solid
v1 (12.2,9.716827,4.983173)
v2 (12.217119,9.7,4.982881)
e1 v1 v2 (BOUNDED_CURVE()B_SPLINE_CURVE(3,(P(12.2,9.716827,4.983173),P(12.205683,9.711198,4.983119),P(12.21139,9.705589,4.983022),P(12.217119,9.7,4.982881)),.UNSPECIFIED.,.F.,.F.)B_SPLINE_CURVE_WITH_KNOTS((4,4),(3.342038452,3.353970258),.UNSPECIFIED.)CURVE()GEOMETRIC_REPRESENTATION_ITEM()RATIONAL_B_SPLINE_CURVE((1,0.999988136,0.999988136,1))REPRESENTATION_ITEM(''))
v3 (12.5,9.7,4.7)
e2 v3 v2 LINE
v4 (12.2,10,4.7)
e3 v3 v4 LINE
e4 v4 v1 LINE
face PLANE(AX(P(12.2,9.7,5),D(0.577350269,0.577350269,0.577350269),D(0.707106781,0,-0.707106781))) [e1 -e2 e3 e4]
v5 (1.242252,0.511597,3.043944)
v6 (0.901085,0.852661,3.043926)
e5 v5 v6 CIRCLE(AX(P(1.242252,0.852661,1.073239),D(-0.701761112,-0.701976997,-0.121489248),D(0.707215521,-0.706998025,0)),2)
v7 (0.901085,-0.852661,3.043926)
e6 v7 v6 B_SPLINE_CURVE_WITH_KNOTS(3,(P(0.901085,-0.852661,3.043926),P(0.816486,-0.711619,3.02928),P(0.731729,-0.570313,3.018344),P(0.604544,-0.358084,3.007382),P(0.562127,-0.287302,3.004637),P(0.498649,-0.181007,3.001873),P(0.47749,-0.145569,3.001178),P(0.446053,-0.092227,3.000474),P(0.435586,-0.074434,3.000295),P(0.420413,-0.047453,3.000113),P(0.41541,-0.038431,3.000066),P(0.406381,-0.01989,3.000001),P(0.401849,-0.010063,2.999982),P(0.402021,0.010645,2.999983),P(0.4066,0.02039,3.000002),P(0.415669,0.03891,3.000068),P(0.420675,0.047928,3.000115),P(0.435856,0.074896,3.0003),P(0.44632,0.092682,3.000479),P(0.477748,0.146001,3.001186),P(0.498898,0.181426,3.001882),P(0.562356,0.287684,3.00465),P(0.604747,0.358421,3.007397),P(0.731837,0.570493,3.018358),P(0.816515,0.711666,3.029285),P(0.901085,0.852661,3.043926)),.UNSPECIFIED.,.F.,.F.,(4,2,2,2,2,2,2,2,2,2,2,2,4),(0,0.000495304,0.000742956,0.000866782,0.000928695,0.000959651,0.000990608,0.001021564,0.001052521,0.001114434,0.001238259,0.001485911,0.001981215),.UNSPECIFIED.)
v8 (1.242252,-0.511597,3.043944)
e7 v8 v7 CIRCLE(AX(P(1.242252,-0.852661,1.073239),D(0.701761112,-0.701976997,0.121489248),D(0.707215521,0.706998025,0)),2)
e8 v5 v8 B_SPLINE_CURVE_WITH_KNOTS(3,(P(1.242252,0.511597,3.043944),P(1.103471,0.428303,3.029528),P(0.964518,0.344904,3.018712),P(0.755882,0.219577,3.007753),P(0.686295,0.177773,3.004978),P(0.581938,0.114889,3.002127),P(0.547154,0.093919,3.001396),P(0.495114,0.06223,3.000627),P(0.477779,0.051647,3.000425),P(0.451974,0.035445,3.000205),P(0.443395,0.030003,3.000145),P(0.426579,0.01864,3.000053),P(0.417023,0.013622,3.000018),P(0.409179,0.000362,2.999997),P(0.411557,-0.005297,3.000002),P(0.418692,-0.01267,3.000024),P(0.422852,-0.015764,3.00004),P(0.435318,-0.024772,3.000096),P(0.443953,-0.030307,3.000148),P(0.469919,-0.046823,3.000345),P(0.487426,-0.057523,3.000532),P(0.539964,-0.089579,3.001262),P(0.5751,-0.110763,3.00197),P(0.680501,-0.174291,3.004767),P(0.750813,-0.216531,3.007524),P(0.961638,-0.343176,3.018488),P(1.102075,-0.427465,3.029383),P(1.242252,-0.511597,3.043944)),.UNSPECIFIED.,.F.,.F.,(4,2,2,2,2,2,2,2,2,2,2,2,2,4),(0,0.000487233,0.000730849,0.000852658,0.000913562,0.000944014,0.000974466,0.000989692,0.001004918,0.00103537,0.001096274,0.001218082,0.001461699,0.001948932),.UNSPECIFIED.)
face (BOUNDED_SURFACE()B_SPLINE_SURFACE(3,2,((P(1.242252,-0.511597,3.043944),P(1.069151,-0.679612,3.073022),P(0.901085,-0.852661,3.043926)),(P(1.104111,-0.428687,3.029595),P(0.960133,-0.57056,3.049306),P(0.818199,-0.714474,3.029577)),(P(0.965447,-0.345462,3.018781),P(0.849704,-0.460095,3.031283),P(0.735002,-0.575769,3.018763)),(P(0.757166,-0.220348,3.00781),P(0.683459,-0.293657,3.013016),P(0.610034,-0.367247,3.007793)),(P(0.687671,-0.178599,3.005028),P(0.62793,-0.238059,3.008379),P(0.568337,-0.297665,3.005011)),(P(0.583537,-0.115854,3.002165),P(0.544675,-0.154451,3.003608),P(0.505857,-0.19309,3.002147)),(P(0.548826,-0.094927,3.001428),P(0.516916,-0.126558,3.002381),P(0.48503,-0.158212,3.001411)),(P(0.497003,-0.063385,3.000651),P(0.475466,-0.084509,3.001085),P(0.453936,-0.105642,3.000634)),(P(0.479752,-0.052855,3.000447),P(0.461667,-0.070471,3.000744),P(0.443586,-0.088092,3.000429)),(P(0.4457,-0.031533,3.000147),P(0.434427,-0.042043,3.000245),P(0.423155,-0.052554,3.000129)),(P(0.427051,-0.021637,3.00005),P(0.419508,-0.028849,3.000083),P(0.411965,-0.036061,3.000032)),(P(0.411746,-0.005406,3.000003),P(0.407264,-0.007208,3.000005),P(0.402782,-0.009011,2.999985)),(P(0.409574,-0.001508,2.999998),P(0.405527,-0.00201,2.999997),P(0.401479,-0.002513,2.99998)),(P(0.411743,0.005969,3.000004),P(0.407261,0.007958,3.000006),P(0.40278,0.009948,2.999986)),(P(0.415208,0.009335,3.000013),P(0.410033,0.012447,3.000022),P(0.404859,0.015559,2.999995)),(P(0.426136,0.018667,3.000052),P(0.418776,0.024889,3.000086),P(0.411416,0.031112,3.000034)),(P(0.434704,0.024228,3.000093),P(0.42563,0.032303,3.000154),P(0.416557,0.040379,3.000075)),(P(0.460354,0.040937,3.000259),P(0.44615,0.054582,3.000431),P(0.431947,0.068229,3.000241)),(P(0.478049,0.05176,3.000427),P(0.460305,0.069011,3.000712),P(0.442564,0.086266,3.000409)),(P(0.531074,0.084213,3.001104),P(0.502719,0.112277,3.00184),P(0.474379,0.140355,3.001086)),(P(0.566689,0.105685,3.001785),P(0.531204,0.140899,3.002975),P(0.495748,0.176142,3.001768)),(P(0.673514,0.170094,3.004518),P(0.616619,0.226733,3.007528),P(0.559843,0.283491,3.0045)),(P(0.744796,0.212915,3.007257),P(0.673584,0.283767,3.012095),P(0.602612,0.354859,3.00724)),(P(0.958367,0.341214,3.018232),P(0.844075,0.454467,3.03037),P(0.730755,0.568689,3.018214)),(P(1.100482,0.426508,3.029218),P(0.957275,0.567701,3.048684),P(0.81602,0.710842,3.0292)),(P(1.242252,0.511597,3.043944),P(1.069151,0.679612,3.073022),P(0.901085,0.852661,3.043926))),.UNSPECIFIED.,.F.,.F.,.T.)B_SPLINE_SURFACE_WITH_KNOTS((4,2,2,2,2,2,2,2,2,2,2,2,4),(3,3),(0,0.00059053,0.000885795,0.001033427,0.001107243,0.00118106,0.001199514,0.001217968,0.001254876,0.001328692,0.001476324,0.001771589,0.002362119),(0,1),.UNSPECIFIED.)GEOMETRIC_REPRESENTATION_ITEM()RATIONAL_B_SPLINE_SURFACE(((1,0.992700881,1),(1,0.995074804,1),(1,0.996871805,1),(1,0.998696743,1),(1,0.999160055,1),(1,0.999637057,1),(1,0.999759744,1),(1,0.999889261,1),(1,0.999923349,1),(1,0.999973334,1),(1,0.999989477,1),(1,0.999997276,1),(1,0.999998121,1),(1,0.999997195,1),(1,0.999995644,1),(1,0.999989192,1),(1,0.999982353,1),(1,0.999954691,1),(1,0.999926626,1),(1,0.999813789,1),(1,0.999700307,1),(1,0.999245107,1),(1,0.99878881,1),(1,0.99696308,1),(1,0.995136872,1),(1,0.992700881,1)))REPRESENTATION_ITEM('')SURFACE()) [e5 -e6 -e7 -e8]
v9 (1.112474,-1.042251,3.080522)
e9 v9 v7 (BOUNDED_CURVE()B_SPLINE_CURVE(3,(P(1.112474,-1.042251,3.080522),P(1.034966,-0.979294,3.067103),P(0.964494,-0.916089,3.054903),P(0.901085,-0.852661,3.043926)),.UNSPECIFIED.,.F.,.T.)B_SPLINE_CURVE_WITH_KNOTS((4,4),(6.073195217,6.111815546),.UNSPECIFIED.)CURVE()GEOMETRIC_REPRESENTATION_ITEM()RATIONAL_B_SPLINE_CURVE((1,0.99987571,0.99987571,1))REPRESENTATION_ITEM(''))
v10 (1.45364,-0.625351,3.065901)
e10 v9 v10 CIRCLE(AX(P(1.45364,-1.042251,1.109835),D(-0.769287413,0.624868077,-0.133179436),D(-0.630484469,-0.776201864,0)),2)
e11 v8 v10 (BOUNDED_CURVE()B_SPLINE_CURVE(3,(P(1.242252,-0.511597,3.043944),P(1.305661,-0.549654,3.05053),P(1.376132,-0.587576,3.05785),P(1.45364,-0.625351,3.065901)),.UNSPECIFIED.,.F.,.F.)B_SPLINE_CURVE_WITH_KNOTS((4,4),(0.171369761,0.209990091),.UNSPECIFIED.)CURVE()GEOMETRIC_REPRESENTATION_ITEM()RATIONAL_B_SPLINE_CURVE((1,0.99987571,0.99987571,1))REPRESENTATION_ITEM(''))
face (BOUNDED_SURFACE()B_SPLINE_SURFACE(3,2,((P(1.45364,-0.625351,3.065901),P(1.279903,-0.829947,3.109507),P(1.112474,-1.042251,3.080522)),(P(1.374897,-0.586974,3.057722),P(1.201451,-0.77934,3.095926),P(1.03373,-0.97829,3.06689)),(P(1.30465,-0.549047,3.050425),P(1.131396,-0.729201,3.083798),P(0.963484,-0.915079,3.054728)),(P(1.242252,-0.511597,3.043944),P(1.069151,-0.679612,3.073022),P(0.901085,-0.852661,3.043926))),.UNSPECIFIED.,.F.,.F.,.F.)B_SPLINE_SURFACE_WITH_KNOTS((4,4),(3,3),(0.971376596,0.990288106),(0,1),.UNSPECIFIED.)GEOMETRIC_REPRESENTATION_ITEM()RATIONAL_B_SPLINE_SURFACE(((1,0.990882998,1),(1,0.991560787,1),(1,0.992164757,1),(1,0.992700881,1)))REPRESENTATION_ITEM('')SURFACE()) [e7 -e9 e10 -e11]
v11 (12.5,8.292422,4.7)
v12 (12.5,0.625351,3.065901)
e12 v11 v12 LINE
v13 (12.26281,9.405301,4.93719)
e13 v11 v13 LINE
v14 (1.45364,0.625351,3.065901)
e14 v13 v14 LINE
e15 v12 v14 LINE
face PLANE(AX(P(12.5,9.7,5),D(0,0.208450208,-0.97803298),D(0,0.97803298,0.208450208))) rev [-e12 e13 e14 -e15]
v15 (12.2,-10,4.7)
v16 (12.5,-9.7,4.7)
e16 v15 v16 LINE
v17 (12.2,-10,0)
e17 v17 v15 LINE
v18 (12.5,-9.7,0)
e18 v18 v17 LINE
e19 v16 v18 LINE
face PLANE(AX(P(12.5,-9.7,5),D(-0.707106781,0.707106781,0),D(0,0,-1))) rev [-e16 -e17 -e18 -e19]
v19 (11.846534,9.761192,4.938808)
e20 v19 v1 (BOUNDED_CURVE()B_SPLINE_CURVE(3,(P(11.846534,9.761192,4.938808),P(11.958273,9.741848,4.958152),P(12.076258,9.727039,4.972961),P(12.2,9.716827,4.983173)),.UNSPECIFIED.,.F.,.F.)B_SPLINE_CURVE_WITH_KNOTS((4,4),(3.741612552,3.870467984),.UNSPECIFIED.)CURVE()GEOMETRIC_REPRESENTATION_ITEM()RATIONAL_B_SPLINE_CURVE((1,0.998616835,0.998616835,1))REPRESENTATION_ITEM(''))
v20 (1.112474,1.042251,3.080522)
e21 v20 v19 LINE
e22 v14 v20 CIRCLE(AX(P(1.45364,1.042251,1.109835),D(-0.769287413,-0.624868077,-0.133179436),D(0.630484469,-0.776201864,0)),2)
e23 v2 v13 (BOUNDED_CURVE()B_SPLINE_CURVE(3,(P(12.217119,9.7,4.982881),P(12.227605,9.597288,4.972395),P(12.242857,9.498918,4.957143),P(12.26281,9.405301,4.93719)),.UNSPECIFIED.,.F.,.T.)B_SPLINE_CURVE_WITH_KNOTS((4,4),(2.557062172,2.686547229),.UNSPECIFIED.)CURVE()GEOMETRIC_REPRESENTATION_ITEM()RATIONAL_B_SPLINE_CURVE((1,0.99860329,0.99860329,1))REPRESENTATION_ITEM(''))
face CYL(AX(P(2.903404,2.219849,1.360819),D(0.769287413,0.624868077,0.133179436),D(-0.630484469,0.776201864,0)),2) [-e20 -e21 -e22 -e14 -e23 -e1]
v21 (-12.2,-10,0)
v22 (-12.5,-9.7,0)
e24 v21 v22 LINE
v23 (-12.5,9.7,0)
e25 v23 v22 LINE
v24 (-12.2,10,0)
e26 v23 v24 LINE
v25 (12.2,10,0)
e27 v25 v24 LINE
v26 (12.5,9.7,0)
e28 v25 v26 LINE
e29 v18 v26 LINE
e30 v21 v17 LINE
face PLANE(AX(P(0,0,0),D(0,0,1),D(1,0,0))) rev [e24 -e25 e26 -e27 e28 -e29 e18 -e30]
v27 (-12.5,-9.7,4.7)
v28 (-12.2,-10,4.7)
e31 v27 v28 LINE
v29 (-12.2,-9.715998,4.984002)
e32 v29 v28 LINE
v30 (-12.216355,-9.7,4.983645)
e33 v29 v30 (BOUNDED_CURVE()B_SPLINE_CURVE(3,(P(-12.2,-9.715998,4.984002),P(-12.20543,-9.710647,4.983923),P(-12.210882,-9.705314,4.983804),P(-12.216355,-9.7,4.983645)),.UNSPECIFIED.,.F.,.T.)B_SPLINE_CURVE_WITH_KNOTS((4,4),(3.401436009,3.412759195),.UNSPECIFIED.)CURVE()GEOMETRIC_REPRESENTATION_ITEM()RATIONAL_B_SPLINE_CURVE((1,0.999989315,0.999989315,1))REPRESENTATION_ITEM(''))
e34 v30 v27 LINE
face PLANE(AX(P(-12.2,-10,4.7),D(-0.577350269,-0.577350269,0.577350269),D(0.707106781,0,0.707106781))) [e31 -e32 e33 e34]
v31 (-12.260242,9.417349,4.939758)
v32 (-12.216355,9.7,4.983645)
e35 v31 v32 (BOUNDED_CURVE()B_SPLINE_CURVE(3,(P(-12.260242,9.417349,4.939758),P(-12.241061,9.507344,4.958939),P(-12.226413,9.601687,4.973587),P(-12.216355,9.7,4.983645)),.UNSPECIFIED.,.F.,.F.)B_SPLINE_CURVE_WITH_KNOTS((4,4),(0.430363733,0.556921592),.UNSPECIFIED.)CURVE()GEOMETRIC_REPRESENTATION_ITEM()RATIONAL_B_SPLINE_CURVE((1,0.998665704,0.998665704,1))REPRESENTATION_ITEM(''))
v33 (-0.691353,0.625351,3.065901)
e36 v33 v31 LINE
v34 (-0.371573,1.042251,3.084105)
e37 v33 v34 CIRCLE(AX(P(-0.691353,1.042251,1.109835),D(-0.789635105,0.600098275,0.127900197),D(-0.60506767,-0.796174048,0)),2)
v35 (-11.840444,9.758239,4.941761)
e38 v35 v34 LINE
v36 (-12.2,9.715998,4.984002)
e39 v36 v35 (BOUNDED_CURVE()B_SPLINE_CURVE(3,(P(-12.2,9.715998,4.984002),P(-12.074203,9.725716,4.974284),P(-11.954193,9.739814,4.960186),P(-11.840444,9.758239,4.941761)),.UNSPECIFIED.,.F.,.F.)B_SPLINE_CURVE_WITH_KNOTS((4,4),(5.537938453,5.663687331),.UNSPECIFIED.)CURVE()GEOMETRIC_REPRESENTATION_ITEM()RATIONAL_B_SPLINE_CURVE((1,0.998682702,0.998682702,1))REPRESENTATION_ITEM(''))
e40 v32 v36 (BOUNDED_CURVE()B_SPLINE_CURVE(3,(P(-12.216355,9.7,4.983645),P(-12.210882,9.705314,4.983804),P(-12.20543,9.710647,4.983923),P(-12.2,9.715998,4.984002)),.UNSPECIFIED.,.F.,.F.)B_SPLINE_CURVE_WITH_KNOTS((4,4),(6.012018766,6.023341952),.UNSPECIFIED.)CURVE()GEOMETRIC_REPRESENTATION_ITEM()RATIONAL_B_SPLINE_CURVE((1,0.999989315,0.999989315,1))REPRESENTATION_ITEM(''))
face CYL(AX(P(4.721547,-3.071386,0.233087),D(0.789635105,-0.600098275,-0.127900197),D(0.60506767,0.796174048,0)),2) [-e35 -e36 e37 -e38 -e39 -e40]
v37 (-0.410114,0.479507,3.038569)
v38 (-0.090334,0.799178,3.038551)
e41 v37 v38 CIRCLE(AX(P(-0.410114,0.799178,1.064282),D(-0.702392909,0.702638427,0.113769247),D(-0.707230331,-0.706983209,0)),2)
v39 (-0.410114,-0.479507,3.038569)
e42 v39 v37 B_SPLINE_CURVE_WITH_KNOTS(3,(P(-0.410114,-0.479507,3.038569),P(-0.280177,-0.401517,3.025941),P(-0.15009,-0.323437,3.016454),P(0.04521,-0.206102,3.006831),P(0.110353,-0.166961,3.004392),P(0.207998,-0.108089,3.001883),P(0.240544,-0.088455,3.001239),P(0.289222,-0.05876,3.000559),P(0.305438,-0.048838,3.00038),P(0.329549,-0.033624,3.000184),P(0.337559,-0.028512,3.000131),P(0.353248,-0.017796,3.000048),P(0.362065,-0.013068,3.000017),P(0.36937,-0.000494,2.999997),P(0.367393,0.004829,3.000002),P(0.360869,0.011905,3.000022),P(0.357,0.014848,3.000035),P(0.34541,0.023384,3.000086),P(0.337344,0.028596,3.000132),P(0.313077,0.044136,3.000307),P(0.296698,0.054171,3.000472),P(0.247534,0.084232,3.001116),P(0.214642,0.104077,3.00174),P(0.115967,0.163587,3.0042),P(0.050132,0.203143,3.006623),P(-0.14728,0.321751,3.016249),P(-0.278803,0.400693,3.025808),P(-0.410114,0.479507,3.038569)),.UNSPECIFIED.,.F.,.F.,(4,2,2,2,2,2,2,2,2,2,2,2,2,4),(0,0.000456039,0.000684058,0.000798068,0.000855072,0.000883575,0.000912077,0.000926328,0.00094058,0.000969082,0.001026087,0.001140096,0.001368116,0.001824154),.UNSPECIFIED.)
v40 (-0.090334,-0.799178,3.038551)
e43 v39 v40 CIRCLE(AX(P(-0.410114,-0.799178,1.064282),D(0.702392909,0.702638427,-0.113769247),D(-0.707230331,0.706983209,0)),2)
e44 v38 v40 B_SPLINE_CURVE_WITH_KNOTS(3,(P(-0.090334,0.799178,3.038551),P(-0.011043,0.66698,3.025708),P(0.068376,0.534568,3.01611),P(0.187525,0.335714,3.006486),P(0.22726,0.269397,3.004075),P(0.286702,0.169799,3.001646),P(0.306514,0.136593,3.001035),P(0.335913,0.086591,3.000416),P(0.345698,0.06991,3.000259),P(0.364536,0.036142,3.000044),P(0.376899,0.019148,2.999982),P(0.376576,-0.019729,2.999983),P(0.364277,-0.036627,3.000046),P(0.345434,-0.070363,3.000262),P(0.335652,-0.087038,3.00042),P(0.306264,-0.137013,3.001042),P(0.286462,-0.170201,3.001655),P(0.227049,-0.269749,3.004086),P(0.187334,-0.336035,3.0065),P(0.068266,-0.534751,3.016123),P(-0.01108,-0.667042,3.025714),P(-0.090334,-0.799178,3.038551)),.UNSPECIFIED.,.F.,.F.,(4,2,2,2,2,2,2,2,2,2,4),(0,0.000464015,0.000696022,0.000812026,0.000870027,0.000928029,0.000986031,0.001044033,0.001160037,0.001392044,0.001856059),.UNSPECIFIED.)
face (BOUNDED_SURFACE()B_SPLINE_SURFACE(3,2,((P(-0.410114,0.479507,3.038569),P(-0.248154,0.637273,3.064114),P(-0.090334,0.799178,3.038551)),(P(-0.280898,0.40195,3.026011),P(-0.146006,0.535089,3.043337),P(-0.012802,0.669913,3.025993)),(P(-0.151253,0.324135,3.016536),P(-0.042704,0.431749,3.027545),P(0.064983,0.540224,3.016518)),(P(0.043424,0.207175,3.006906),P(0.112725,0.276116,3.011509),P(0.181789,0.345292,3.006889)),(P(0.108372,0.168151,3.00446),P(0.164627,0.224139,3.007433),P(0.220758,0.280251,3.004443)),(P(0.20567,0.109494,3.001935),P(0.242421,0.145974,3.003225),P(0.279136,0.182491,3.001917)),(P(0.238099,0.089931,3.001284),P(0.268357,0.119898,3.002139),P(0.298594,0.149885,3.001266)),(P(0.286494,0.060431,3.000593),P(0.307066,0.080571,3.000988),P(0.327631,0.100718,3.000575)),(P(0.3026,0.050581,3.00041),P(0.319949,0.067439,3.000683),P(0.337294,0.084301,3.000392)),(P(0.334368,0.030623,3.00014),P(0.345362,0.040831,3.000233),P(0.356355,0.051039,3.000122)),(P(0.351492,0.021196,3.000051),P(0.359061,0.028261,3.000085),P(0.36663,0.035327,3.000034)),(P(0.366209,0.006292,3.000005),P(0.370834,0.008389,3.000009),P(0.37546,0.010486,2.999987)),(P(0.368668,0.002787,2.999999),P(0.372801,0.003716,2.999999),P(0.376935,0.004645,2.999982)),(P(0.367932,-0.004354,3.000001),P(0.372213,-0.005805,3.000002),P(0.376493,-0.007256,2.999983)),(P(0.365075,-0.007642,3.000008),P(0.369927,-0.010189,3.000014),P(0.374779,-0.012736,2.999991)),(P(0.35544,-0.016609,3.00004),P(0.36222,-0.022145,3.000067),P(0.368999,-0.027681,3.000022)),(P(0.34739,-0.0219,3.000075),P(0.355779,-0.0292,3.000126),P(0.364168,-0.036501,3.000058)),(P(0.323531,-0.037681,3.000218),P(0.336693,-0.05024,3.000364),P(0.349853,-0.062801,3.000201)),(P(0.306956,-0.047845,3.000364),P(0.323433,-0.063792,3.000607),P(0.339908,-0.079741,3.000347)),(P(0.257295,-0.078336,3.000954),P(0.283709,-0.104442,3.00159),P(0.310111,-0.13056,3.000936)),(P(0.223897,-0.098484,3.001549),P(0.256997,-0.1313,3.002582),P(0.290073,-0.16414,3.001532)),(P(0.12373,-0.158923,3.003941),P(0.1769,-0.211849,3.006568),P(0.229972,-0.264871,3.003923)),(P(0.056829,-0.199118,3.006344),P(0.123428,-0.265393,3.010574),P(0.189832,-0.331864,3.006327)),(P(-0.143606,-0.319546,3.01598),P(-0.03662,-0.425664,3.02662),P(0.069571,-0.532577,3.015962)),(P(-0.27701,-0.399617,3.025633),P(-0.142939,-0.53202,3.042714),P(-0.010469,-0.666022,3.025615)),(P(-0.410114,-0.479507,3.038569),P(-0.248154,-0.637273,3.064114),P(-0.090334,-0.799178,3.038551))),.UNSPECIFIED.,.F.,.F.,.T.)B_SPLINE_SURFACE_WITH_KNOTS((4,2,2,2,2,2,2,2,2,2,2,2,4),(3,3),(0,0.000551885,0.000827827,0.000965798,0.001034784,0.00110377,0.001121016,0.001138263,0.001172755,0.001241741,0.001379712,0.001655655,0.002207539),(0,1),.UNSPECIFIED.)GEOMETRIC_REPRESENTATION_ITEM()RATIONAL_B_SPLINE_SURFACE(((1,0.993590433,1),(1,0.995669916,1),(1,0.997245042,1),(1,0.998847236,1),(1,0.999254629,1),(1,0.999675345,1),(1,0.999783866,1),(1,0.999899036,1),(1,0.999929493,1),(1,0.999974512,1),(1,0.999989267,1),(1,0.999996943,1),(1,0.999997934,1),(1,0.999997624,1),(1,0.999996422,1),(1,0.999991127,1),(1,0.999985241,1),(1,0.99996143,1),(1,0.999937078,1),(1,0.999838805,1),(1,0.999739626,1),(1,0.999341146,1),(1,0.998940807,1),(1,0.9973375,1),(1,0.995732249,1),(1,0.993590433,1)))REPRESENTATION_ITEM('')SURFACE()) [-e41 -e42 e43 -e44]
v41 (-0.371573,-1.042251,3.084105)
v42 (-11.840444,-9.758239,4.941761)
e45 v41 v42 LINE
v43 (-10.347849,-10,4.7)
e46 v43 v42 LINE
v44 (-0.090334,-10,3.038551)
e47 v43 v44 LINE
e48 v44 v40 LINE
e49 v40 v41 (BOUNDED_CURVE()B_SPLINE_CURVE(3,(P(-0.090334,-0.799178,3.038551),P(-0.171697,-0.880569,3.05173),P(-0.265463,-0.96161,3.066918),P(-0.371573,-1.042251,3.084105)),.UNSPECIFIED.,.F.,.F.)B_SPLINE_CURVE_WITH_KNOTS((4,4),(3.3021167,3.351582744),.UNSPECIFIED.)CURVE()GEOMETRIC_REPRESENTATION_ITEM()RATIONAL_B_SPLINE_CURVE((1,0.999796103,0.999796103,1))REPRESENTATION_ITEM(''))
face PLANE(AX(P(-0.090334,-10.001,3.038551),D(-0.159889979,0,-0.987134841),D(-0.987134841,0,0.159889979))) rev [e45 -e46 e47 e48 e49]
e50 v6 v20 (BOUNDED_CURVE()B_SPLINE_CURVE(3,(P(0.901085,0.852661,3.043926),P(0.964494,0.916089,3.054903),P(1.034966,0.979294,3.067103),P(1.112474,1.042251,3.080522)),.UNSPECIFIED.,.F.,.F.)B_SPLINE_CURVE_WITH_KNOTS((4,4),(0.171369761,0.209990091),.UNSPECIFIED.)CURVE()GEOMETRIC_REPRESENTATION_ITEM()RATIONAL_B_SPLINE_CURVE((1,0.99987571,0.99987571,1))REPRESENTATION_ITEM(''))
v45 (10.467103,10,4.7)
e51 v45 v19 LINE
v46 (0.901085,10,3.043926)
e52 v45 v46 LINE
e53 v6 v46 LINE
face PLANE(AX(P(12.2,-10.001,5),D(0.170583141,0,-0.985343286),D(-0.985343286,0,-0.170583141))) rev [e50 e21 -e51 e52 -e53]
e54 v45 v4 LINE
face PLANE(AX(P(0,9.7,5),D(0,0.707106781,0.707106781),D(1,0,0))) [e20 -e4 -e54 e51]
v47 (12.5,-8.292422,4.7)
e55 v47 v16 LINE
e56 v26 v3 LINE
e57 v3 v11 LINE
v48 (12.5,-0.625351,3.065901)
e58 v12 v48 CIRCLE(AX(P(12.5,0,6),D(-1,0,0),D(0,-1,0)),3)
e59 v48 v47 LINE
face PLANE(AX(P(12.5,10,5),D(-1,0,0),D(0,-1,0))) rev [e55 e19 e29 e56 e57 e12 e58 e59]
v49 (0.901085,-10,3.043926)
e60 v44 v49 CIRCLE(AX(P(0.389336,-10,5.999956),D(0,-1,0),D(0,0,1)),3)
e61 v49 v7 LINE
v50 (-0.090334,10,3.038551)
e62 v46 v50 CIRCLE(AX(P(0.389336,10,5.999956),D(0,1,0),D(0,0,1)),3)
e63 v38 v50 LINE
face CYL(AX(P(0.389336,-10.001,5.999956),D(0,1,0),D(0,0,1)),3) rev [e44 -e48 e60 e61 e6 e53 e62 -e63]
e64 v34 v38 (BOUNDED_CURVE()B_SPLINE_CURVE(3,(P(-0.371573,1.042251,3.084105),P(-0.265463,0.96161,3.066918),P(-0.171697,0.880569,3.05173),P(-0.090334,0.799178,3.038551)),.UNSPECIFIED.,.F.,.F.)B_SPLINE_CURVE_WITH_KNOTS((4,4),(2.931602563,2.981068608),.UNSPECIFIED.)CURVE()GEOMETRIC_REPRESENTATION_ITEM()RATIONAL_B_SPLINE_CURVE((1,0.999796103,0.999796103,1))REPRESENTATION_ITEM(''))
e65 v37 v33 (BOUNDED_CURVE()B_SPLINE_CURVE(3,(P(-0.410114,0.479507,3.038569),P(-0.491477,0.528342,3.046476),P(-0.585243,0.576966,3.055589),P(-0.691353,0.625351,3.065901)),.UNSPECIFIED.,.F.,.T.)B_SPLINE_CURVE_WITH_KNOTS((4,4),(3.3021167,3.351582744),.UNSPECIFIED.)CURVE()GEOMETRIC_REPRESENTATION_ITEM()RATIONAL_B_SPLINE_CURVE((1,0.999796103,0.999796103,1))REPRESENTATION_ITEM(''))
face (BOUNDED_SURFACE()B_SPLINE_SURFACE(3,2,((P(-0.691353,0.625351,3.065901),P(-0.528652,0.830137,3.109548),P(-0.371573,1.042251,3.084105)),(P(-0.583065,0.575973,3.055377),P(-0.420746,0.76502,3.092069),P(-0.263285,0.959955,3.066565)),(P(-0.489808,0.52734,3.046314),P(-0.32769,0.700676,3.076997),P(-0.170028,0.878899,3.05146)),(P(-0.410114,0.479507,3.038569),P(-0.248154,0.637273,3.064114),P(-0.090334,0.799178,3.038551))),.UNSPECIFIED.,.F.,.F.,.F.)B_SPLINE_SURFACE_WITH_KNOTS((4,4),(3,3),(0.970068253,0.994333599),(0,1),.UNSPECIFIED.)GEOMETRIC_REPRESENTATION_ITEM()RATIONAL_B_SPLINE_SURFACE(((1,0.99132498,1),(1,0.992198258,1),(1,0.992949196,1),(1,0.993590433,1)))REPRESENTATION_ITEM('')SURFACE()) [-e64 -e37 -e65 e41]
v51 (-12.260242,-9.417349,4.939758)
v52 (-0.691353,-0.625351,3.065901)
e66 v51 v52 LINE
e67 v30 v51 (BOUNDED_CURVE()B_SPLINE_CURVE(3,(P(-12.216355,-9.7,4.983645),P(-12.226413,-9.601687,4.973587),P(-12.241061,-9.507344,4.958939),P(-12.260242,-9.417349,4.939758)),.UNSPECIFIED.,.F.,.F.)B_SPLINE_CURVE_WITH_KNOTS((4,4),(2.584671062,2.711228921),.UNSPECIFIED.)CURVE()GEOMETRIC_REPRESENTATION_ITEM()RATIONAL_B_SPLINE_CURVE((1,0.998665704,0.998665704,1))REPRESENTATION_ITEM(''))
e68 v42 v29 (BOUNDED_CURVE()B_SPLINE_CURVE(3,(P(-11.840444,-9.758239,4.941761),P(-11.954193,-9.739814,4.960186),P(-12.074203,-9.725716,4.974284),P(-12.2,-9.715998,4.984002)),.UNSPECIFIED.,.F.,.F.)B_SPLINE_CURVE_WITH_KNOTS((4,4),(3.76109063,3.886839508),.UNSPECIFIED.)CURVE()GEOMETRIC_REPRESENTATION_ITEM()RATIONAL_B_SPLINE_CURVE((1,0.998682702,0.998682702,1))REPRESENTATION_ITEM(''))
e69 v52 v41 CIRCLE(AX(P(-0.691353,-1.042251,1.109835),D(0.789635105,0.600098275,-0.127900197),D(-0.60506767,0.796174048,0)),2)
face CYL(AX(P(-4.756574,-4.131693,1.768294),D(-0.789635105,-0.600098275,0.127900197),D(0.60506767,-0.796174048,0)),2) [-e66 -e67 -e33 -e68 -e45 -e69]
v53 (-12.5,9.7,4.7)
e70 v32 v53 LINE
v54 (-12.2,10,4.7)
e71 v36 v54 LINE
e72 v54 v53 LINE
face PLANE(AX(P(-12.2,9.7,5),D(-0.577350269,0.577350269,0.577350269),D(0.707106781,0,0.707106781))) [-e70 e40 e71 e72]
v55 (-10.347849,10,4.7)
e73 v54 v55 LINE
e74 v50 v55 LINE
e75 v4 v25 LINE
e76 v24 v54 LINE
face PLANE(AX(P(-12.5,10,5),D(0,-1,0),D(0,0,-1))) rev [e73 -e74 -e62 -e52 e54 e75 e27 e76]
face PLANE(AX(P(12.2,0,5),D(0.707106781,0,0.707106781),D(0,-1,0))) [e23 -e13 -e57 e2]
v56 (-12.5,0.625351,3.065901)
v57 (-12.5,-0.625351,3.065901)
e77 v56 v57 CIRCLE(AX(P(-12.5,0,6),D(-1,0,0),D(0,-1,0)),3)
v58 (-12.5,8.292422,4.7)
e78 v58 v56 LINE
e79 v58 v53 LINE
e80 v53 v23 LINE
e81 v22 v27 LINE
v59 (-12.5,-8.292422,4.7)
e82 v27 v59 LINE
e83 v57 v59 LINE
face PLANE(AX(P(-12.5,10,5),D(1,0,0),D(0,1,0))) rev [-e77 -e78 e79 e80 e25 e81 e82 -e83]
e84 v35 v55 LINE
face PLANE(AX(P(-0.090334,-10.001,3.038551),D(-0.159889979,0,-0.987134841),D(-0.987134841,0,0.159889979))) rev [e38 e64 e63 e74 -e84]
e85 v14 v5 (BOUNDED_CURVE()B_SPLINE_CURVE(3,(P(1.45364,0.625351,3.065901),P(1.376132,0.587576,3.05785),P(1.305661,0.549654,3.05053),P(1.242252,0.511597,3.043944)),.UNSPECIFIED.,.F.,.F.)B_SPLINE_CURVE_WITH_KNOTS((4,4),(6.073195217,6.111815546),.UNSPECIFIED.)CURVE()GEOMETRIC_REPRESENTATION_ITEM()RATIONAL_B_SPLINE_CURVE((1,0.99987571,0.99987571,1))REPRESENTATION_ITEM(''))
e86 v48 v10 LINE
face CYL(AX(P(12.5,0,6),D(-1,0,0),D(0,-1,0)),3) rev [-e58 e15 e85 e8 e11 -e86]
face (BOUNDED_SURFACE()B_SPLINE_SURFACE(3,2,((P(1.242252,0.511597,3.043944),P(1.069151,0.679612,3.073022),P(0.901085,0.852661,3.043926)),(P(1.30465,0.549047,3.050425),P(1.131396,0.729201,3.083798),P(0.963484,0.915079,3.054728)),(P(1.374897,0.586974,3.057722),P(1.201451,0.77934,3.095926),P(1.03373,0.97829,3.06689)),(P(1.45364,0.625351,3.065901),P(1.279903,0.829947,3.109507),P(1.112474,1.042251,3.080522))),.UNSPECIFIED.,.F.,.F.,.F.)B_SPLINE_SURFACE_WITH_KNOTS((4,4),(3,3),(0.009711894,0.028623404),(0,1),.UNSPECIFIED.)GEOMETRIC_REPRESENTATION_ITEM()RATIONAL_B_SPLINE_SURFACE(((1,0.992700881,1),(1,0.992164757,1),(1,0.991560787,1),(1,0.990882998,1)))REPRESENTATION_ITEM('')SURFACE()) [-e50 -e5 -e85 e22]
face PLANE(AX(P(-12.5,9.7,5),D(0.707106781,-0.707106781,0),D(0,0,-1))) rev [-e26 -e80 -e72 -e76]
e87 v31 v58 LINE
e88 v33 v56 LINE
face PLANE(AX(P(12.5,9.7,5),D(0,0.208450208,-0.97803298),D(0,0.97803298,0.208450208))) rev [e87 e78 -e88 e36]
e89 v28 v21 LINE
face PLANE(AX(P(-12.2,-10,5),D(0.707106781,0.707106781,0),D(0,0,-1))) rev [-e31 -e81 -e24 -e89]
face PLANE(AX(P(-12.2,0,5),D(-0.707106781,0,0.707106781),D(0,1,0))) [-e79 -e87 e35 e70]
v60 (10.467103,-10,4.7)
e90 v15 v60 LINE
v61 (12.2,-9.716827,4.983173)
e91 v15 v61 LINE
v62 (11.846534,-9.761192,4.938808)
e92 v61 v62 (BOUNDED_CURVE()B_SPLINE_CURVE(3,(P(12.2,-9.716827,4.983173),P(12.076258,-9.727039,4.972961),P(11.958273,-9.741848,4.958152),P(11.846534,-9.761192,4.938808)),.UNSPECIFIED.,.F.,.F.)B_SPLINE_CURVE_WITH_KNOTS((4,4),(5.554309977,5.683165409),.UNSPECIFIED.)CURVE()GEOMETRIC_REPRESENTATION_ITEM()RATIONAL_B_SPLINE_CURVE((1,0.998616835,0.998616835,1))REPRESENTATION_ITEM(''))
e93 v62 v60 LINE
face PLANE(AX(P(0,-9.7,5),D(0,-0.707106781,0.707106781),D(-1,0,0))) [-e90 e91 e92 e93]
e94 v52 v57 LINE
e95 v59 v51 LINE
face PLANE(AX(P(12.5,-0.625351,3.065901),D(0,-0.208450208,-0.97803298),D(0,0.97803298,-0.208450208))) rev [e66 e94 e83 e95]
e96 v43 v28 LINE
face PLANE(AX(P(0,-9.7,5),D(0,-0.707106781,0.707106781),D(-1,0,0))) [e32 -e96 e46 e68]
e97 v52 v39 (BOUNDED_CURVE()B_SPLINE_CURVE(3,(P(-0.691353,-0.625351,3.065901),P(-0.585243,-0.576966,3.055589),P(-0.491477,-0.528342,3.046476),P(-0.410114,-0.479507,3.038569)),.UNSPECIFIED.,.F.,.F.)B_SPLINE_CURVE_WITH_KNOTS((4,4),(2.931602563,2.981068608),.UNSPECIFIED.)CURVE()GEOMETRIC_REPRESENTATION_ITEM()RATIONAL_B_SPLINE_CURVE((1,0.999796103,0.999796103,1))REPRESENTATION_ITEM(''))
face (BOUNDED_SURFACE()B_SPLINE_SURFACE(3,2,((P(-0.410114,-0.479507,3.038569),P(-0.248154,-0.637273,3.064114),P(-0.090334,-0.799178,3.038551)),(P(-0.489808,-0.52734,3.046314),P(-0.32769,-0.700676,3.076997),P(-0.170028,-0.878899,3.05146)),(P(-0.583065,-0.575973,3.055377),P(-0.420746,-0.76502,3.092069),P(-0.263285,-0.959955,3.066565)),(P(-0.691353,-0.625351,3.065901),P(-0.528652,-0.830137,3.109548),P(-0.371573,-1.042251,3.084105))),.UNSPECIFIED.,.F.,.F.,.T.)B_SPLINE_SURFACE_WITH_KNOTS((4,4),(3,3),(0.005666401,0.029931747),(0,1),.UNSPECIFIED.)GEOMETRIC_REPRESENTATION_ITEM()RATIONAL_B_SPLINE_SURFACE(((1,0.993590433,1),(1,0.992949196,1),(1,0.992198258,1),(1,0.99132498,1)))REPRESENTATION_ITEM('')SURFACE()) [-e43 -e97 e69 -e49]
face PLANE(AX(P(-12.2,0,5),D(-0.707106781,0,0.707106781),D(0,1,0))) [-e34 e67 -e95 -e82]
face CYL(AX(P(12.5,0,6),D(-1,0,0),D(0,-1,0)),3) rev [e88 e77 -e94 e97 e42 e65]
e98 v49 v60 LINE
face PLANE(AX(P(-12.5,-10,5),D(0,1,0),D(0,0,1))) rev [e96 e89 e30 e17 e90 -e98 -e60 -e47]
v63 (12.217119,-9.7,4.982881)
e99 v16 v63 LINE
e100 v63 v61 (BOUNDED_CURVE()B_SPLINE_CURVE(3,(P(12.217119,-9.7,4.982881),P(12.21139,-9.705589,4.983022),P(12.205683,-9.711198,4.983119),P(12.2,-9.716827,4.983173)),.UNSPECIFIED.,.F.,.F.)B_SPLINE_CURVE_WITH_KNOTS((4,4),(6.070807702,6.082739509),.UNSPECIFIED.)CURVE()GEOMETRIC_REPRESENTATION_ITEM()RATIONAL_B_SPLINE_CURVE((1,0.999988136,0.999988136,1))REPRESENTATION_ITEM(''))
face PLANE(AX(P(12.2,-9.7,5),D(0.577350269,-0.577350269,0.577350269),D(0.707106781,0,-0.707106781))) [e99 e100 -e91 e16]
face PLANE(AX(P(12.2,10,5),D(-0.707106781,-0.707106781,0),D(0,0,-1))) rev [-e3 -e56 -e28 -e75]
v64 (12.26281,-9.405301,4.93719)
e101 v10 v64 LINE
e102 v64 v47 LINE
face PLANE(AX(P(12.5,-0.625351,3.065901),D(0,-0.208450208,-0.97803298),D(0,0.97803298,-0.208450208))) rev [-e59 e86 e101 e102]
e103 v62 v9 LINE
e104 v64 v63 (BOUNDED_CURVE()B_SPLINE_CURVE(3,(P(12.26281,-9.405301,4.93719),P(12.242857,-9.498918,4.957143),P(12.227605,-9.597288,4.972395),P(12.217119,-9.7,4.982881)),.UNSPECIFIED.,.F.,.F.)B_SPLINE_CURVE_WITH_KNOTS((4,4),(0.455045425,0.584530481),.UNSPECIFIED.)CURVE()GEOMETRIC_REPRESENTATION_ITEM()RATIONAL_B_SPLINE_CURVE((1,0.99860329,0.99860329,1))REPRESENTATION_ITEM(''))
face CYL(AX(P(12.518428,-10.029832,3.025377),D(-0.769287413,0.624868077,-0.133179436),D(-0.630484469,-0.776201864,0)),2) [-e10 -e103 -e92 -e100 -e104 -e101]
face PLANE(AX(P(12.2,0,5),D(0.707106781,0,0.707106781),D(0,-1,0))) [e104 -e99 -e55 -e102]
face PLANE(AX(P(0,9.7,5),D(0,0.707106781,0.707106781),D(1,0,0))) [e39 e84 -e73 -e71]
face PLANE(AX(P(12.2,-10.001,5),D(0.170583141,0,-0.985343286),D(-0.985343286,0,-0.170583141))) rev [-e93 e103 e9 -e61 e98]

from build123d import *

# Parameters (mm, degrees)
SKETCH1_W           = 25
SKETCH1_H           = 20
BOSS_EXTRUDE1_DEPTH = 5
CHAMFER1_SIZE       = 0.3
CUT_EXTRUDE1_REACH  = 26.109
CUT_EXTRUDE2_DEPTH  = 28.386127875
FILLET1_R           = 2


with BuildPart() as part:
    # Sketch1 → Boss-Extrude1 (new body)
    with BuildSketch(Plane.XY):
        Rectangle(SKETCH1_W, SKETCH1_H)
    extrude(amount=BOSS_EXTRUDE1_DEPTH)

    # Chamfer1
    chamfer1_edges = [part.edges().sort_by_distance(p)[0] for p in [
        (-12.5, 0, 5),
        (0, -10, 5),
        (12.5, 0, 5),
        (12.5, -10, 2.5),
        (-12.5, -10, 2.5),
        (-12.5, 10, 2.5),
        (12.5, 10, 2.5),
        (0, 10, 5),
    ]]
    chamfer(chamfer1_edges, length=CHAMFER1_SIZE)

    # Sketch2 → Cut-Extrude1 (cut, up to next)
    with BuildSketch(Plane(origin=(0, 10, 0), x_dir=(1, 0, 0), z_dir=(0, 1, 0)), mode=Mode.PRIVATE) as cut_extrude1_sk1:
        with BuildLine():
            Line((12.2, -5), (0.90108548, -3.043926058))
            ThreePointArc((0.90108548, -3.043926058), (0.405599363, -3), (-0.090333879, -3.038551394))
            Line((-0.090333879, -3.038551394), (-12.2, -5))
            Line((-12.2, -5), (12.2, -5))
        make_face()
    cut_extrude1_tool1 = extrude(cut_extrude1_sk1.sketch, amount=-CUT_EXTRUDE1_REACH, mode=Mode.PRIVATE) & part.part
    add(cut_extrude1_tool1.solids().sort_by_distance((0.135125, 10, 4.320136))[0], mode=Mode.SUBTRACT)

    # Sketch3 → Cut-Extrude2 (cut, through all)
    with BuildSketch(Plane.ZY.offset(12.5)):
        with BuildLine():
            Line((5, 9.7), (3.065901059, 0.625350625))
            ThreePointArc((3.065901059, 0.625350625), (3, 0), (3.065901059, -0.625350625))
            Line((3.065901059, -0.625350625), (5, -9.7))
            Line((5, -9.7), (5, 9.7))
        make_face()
    extrude(amount=-CUT_EXTRUDE2_DEPTH, mode=Mode.SUBTRACT)

    # Fillet1
    fillet1_edges = [part.edges().sort_by_distance(p)[0] for p in [
        (6.61401009, 5.162675312, 4.032950529),
        (0.963107155, 0.570080363, 3.054663282),
        (0.963107155, -0.570080363, 3.054663282),
        (6.61401009, -5.162675312, 4.032950529),
        (-6.229593142, -5.162675312, 4.032950529),
        (-0.172328062, 0.555254202, 3.051832303),
        (0.373072756, -2e-09, 3),
        (-0.172328062, -0.555254202, 3.051832303),
        (0.405599358, -2e-09, 3),
        (-6.229593142, 5.162675312, 4.032950529),
    ]]
    fillet(fillet1_edges, radius=FILLET1_R)


solid = part.part
